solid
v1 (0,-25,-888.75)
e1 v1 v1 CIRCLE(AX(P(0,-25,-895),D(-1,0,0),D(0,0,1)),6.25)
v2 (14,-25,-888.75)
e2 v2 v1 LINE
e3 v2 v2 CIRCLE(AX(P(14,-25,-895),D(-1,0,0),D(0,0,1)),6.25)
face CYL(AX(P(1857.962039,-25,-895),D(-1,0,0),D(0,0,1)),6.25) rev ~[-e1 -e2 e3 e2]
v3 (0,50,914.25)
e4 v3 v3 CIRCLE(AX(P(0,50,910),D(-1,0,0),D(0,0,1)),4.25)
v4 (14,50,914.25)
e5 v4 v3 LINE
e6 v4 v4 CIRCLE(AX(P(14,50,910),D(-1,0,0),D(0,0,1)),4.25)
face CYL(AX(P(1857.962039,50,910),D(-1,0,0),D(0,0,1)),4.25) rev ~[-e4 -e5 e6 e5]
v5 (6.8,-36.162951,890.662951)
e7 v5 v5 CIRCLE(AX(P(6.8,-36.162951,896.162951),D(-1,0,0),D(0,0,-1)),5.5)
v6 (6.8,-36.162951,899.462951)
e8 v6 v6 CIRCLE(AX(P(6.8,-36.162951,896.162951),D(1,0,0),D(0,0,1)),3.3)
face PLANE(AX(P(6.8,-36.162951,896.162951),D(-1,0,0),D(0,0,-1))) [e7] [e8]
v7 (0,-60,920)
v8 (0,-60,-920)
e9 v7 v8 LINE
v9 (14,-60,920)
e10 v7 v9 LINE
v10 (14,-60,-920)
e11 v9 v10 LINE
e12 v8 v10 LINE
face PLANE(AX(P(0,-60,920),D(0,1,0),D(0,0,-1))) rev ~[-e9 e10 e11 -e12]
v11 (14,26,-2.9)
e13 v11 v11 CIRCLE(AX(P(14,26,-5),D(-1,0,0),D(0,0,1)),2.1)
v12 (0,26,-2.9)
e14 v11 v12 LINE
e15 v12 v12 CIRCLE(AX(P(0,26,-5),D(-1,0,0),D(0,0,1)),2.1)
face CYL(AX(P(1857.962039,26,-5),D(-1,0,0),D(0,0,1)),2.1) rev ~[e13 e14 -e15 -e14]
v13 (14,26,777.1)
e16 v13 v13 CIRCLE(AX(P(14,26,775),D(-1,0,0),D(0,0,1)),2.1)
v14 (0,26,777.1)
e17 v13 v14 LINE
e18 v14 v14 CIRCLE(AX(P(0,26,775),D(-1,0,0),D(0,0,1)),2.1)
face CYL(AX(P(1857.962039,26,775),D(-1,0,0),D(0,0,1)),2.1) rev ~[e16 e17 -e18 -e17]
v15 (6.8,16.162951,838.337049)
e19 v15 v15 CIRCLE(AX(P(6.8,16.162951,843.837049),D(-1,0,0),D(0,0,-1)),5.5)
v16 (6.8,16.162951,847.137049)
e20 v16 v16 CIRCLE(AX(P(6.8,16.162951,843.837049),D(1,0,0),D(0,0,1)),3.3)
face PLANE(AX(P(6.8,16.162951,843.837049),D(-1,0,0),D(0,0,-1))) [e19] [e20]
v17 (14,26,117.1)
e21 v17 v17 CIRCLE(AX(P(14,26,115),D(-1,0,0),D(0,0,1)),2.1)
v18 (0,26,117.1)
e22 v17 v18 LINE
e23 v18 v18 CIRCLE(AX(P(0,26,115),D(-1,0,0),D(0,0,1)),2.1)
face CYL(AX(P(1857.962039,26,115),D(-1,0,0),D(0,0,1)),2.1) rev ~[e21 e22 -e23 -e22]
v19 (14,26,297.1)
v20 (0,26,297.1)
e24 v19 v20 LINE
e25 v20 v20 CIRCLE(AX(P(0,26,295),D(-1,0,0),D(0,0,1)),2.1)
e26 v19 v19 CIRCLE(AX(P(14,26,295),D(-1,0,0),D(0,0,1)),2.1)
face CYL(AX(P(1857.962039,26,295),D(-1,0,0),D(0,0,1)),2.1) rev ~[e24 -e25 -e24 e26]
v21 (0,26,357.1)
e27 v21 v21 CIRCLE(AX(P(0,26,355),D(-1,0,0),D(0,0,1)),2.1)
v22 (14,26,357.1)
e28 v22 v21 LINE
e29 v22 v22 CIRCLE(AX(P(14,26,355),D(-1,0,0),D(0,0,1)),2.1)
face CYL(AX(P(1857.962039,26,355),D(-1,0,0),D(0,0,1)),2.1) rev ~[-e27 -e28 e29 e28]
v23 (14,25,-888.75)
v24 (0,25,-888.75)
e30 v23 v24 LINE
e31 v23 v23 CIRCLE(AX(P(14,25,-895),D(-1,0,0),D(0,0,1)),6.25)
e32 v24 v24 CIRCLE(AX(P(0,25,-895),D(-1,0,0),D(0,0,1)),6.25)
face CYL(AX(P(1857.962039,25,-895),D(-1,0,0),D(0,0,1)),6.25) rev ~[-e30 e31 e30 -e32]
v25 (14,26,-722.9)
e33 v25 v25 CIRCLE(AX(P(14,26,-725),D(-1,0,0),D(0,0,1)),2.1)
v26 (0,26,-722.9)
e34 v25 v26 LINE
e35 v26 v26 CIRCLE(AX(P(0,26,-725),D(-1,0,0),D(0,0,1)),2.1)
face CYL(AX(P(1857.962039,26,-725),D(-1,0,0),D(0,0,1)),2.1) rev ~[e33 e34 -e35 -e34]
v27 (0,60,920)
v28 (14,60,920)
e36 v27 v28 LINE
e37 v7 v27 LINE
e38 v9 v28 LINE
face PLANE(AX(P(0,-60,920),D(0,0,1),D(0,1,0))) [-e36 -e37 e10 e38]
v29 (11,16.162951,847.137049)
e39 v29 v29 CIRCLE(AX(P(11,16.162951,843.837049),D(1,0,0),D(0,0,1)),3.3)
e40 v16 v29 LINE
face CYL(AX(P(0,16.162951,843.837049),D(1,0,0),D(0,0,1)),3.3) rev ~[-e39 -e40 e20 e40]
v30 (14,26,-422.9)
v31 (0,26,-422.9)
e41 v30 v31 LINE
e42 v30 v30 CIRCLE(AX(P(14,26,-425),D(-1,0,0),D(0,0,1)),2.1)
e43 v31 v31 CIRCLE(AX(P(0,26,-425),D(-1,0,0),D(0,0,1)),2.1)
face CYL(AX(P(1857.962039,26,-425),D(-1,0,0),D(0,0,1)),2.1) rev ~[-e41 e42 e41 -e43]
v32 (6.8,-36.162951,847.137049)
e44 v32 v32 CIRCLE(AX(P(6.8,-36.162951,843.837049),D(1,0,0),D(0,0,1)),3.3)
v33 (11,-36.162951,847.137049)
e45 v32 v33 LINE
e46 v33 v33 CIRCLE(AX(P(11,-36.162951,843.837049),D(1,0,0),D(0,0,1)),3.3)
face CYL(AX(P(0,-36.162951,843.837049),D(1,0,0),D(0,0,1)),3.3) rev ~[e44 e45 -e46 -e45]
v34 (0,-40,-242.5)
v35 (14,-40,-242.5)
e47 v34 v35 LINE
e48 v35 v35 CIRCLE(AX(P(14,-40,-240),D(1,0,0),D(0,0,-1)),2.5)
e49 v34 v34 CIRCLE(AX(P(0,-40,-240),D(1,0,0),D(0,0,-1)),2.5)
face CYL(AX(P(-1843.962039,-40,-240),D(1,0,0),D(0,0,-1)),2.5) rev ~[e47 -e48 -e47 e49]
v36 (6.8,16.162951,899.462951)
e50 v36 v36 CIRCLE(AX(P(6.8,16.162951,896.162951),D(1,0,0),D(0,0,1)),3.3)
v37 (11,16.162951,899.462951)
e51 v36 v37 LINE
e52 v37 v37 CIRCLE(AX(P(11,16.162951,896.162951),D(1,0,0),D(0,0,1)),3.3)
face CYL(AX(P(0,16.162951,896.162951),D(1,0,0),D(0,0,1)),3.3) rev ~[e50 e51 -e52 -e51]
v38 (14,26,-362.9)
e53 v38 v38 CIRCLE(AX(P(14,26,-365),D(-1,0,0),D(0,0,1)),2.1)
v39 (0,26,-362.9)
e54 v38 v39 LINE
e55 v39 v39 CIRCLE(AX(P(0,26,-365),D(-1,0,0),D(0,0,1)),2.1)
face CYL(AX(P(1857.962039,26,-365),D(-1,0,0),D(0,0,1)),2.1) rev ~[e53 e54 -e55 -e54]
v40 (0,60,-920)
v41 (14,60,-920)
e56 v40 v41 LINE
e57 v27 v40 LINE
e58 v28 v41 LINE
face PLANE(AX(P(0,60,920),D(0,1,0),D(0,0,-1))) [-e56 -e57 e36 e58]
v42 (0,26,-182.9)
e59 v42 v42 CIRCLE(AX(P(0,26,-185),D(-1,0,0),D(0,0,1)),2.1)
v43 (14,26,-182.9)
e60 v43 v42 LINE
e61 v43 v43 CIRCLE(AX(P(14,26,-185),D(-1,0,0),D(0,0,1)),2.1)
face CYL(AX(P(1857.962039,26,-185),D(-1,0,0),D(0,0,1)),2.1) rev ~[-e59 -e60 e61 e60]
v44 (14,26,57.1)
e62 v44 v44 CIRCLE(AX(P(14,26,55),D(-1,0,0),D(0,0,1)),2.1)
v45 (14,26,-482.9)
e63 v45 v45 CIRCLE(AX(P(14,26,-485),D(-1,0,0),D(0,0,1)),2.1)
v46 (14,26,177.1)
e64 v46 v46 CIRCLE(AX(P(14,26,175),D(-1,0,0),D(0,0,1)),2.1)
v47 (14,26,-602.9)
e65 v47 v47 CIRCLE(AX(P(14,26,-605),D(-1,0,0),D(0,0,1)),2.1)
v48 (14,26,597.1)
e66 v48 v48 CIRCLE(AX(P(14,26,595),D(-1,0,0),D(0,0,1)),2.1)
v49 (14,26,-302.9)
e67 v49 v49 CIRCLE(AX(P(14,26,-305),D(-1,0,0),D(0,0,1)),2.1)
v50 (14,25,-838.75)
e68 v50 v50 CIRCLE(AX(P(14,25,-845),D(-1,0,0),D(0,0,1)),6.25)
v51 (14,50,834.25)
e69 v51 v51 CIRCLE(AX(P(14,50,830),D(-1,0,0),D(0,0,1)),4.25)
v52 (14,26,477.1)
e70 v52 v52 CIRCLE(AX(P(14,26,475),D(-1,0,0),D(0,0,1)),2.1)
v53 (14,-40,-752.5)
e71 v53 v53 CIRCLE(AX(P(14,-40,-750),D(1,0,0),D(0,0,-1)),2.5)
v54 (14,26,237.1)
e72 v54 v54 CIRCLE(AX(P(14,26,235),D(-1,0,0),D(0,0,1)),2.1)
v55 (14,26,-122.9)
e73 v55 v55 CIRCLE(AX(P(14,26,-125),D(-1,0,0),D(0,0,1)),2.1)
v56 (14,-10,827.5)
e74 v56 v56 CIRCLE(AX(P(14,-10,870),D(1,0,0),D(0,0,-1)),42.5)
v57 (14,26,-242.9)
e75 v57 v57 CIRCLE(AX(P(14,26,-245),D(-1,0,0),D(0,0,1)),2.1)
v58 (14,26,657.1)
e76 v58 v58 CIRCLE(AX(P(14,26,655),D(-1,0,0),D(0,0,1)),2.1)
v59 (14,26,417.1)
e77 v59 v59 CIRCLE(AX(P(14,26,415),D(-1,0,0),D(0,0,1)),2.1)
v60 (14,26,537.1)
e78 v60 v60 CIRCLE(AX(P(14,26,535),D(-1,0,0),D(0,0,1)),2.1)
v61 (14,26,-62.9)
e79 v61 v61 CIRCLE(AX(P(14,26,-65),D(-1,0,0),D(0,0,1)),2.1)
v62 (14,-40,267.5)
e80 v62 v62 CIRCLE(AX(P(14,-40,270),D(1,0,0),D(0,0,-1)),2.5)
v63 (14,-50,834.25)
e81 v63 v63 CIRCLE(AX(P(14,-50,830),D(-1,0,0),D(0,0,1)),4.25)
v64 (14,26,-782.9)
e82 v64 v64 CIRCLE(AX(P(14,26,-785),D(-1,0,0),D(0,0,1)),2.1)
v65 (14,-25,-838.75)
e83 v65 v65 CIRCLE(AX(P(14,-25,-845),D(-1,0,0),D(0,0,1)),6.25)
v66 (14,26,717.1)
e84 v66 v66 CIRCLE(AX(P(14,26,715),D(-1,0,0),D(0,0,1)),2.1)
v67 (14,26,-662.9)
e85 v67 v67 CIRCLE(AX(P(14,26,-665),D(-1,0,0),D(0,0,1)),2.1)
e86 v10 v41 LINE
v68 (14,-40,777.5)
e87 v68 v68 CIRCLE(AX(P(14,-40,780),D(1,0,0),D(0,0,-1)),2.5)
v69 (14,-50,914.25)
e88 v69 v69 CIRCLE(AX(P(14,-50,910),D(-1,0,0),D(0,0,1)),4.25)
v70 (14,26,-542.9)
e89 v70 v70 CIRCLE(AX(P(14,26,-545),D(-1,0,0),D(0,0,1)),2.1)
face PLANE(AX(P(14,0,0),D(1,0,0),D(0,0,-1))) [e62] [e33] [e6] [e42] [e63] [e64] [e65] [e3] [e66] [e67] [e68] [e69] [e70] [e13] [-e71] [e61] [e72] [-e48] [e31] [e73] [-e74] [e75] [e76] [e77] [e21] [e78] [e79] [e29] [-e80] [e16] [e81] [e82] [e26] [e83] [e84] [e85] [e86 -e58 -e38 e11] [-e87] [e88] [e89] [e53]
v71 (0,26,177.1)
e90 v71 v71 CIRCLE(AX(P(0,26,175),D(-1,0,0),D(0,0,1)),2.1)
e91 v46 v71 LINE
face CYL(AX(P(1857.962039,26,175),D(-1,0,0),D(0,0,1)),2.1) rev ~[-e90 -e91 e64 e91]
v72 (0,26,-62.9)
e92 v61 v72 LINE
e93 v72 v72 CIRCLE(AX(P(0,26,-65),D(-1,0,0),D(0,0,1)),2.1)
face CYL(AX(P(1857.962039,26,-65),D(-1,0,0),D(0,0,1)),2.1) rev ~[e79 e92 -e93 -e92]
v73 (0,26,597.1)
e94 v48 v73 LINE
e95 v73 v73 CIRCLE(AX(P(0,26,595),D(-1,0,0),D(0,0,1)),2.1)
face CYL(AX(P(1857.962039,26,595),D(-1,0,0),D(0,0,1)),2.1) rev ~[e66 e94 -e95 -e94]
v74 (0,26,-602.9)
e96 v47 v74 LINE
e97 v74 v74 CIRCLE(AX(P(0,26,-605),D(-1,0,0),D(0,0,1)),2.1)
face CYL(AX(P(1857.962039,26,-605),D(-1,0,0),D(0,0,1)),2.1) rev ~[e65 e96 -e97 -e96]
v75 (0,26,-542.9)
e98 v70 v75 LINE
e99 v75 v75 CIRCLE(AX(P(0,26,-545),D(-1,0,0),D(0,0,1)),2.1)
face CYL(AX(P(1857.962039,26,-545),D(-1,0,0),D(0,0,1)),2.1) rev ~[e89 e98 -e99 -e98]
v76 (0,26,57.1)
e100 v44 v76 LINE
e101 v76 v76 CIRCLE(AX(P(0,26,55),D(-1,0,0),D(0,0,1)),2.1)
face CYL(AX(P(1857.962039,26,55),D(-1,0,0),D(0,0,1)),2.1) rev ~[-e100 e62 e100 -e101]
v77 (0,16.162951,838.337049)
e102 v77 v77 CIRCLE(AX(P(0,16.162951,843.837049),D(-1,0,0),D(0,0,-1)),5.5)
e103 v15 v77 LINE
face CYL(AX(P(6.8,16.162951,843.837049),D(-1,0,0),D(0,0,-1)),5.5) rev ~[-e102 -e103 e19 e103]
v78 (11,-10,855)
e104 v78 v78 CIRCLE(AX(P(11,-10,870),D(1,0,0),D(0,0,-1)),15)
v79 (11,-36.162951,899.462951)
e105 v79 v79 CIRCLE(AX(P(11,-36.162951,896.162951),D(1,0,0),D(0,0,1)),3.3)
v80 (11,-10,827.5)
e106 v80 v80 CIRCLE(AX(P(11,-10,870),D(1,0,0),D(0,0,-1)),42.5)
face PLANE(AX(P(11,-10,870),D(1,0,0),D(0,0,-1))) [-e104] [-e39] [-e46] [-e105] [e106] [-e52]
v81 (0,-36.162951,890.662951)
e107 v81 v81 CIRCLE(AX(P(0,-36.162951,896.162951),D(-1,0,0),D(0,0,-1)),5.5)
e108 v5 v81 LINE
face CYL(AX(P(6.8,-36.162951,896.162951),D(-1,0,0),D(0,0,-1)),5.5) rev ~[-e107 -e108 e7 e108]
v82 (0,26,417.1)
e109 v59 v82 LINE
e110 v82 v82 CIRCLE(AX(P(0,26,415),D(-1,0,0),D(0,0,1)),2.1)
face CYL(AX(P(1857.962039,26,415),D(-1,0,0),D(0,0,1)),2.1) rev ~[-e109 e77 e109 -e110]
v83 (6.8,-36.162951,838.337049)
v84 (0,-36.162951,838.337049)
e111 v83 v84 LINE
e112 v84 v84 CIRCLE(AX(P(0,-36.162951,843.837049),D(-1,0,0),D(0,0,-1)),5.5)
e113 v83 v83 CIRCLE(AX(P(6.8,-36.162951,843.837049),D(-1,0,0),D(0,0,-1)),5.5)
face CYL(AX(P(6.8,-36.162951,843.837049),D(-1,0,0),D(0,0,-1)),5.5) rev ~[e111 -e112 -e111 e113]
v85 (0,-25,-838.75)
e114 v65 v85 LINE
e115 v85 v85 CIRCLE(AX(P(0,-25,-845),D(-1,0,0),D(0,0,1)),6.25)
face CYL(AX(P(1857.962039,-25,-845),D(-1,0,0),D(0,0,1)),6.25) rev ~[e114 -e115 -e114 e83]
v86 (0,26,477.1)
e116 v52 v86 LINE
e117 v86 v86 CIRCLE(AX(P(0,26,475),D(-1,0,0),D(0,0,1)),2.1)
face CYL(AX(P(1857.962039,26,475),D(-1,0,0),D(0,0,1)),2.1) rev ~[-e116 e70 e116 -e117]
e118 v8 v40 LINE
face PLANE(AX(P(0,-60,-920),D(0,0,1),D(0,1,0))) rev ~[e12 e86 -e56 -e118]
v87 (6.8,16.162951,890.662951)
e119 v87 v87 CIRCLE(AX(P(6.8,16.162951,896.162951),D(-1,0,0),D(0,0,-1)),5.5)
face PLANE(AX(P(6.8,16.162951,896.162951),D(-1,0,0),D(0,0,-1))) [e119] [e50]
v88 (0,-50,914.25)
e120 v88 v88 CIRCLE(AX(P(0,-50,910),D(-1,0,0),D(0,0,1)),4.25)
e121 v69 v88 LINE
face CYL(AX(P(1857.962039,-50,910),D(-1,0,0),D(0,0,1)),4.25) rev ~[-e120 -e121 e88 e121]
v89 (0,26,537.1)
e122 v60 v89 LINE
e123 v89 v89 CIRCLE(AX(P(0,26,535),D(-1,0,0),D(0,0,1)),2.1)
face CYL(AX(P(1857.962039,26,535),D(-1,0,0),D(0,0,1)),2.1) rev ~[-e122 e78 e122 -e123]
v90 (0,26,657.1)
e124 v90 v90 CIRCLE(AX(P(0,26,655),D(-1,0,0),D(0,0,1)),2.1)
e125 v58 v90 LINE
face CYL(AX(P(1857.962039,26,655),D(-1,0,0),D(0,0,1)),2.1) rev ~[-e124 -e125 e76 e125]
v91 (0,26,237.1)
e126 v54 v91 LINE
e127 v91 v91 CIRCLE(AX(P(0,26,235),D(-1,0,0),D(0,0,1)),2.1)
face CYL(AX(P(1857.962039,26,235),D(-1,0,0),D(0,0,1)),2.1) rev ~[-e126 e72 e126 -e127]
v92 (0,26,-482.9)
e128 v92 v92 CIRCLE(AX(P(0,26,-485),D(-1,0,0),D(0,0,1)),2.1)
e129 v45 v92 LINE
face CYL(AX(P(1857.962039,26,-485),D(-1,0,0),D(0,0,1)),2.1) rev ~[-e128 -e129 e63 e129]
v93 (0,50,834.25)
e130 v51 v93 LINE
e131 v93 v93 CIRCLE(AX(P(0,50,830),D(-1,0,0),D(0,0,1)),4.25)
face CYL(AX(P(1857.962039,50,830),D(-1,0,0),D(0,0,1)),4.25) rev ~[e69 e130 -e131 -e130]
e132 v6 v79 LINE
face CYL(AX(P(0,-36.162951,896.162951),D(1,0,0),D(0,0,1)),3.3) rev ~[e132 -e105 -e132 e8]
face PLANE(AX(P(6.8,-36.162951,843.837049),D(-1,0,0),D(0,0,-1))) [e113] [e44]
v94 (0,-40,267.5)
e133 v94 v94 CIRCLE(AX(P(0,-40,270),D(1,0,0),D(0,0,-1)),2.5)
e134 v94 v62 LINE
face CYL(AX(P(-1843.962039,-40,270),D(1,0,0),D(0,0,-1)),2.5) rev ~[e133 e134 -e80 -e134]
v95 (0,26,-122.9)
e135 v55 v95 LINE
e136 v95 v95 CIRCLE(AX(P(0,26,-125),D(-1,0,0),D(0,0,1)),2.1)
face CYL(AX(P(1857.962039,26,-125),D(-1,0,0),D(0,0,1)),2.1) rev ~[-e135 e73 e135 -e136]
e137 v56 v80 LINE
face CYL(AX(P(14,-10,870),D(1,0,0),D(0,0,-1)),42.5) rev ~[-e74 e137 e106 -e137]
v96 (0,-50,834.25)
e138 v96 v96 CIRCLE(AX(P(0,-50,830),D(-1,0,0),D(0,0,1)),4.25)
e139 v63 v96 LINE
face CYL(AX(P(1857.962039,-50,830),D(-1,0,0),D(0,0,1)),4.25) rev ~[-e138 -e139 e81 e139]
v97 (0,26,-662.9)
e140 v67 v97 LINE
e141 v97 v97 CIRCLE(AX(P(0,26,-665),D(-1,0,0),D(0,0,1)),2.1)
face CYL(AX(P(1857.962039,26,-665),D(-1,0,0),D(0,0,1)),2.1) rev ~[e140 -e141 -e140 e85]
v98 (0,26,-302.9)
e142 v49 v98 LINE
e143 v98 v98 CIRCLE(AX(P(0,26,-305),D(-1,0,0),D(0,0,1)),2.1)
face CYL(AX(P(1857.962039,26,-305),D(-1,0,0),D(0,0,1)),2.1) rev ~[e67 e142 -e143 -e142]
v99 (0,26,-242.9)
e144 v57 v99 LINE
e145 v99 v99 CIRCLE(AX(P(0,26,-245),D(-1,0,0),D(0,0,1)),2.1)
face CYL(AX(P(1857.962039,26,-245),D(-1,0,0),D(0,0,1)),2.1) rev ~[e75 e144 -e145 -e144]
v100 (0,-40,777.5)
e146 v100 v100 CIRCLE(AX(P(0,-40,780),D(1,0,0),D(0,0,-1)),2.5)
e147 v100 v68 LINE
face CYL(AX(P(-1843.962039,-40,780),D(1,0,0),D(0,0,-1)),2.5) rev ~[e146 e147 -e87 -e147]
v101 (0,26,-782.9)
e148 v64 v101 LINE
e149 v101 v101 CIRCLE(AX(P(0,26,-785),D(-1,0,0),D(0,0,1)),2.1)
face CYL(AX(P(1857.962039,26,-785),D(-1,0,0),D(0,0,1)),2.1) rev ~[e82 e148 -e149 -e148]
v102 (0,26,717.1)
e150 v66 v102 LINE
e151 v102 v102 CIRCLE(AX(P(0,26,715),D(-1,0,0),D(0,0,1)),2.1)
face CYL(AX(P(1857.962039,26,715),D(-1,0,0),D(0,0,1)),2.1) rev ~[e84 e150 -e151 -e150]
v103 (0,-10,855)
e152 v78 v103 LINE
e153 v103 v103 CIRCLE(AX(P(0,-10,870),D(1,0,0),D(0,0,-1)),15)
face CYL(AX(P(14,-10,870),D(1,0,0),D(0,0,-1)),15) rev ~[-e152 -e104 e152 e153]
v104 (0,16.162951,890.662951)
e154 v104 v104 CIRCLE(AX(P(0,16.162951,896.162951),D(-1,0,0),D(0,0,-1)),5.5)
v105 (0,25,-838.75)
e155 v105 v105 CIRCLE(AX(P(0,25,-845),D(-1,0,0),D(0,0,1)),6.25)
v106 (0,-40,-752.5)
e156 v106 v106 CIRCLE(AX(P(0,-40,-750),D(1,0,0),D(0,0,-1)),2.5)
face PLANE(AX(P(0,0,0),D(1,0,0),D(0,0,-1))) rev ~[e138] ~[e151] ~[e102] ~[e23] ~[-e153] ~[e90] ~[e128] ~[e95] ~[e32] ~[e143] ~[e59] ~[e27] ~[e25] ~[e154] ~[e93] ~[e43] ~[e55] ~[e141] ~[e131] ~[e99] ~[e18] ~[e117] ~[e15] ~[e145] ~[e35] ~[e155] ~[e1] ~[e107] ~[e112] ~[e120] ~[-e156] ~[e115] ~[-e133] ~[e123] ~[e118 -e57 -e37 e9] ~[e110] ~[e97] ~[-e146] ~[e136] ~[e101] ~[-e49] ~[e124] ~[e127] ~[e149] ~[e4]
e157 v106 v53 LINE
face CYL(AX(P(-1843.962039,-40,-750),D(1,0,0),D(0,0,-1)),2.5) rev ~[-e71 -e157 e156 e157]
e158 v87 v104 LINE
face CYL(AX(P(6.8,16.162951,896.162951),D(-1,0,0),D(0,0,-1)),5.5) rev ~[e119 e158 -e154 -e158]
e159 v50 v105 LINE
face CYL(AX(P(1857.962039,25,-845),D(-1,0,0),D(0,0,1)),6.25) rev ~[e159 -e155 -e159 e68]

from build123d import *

# Parameters (mm, degrees)
SKETCH_1_W                = 1840
SKETCH_1_H                = 120
EXTRUDE_1_DEPTH           = 14
HOLE_WIZARD_1_D           = 6.6
HOLE_WIZARD_1_CBORE_D     = 11
HOLE_WIZARD_1_CBORE_DEPTH = 6.8
HOLE_WIZARD_M5_1_D        = 4.2
PATTERN_LINEAR_1_COUNT    = 27
PATTERN_LINEAR_1_PITCH    = 60
HOLE_WIZARD_12_5_12_5_2_D = 12.5
SKETCH_8_R                = 15
CUT_EXTRUDE_1_DEPTH       = 923.060735527
HOLE_WIZARD_M6_1_D        = 5
PATTERN_LINEAR_2_COUNT    = 4
PATTERN_LINEAR_2_PITCH    = 510
HOLE_WIZARD_8_5_8_5_1_D   = 8.5
SKETCH_13_R               = 42.5
CUT_EXTRUDE_2_DEPTH       = 3


with BuildPart() as part:
    # 草图1 → 凸台-拉伸1 (new body)
    with BuildSketch(Plane(origin=(0, 0, 0), x_dir=(0, 0, -1), z_dir=(1, 0, 0))):
        Rectangle(SKETCH_1_W, SKETCH_1_H)
    extrude(amount=EXTRUDE_1_DEPTH)

    # 打孔尺寸(%根据)内六角圆柱头螺钉的类型1 (through all)
    with Locations(Plane(origin=(0, 0, 0), x_dir=(0, 0, -1), z_dir=(-1, 0, 0))):
        with Locations((-896.162950904, -16.162950904), (-843.837049096, -16.162950904), (-896.162950904, 36.162950904), (-843.837049096, 36.162950904)):
            CounterBoreHole(HOLE_WIZARD_1_D / 2, HOLE_WIZARD_1_CBORE_D / 2, HOLE_WIZARD_1_CBORE_DEPTH)

    # M5 螺纹孔1 (through all)
    with Locations(Plane(origin=(14, 0, 0), x_dir=(0, 0, -1), z_dir=(1, 0, 0))):
        with Locations((-775, 26)):
            hole_wizard_m5_1 = Hole(HOLE_WIZARD_M5_1_D / 2)

    # 阵列(线性)1: M5 螺纹孔1 ×27
    with Locations(*[(0, 0, -i * PATTERN_LINEAR_1_PITCH) for i in range(1, PATTERN_LINEAR_1_COUNT)]):
        add(hole_wizard_m5_1, mode=Mode.SUBTRACT)

    # Ø12.5 (12.5) 直径孔2 (through all)
    with Locations(Plane(origin=(14, 0, 0), x_dir=(0, 0, -1), z_dir=(1, 0, 0))):
        with Locations((845, 25), (895, 25), (845, -25), (895, -25)):
            Hole(HOLE_WIZARD_12_5_12_5_2_D / 2)

    # 草图8 → 切除-拉伸1 (cut, through all)
    with BuildSketch(Plane(origin=(14, 0, 0), x_dir=(0, 0, -1), z_dir=(1, 0, 0))):
        with Locations((-870, -10)):
            Circle(SKETCH_8_R)
    extrude(amount=-CUT_EXTRUDE_1_DEPTH, mode=Mode.SUBTRACT)

    # M6 螺纹孔1 (through all)
    with Locations(Plane.ZY):
        with Locations((780, -40)):
            hole_wizard_m6_1 = Hole(HOLE_WIZARD_M6_1_D / 2)

    # 阵列(线性)2: M6 螺纹孔1 ×4
    with Locations(*[(0, 0, -i * PATTERN_LINEAR_2_PITCH) for i in range(1, PATTERN_LINEAR_2_COUNT)]):
        add(hole_wizard_m6_1, mode=Mode.SUBTRACT)

    # Ø8.5 (8.5) 直径孔1 (through all)
    with Locations(Plane(origin=(14, 0, 0), x_dir=(0, 0, -1), z_dir=(1, 0, 0))):
        with Locations((-910, 50), (-830, 50), (-910, -50), (-830, -50)):
            Hole(HOLE_WIZARD_8_5_8_5_1_D / 2)

    # 草图13 → 切除-拉伸2 (cut)
    with BuildSketch(Plane(origin=(14, 0, 0), x_dir=(0, 0, -1), z_dir=(1, 0, 0))):
        with Locations((-870, -10)):
            Circle(SKETCH_13_R)
    extrude(amount=-CUT_EXTRUDE_2_DEPTH, mode=Mode.SUBTRACT)


solid = part.part
